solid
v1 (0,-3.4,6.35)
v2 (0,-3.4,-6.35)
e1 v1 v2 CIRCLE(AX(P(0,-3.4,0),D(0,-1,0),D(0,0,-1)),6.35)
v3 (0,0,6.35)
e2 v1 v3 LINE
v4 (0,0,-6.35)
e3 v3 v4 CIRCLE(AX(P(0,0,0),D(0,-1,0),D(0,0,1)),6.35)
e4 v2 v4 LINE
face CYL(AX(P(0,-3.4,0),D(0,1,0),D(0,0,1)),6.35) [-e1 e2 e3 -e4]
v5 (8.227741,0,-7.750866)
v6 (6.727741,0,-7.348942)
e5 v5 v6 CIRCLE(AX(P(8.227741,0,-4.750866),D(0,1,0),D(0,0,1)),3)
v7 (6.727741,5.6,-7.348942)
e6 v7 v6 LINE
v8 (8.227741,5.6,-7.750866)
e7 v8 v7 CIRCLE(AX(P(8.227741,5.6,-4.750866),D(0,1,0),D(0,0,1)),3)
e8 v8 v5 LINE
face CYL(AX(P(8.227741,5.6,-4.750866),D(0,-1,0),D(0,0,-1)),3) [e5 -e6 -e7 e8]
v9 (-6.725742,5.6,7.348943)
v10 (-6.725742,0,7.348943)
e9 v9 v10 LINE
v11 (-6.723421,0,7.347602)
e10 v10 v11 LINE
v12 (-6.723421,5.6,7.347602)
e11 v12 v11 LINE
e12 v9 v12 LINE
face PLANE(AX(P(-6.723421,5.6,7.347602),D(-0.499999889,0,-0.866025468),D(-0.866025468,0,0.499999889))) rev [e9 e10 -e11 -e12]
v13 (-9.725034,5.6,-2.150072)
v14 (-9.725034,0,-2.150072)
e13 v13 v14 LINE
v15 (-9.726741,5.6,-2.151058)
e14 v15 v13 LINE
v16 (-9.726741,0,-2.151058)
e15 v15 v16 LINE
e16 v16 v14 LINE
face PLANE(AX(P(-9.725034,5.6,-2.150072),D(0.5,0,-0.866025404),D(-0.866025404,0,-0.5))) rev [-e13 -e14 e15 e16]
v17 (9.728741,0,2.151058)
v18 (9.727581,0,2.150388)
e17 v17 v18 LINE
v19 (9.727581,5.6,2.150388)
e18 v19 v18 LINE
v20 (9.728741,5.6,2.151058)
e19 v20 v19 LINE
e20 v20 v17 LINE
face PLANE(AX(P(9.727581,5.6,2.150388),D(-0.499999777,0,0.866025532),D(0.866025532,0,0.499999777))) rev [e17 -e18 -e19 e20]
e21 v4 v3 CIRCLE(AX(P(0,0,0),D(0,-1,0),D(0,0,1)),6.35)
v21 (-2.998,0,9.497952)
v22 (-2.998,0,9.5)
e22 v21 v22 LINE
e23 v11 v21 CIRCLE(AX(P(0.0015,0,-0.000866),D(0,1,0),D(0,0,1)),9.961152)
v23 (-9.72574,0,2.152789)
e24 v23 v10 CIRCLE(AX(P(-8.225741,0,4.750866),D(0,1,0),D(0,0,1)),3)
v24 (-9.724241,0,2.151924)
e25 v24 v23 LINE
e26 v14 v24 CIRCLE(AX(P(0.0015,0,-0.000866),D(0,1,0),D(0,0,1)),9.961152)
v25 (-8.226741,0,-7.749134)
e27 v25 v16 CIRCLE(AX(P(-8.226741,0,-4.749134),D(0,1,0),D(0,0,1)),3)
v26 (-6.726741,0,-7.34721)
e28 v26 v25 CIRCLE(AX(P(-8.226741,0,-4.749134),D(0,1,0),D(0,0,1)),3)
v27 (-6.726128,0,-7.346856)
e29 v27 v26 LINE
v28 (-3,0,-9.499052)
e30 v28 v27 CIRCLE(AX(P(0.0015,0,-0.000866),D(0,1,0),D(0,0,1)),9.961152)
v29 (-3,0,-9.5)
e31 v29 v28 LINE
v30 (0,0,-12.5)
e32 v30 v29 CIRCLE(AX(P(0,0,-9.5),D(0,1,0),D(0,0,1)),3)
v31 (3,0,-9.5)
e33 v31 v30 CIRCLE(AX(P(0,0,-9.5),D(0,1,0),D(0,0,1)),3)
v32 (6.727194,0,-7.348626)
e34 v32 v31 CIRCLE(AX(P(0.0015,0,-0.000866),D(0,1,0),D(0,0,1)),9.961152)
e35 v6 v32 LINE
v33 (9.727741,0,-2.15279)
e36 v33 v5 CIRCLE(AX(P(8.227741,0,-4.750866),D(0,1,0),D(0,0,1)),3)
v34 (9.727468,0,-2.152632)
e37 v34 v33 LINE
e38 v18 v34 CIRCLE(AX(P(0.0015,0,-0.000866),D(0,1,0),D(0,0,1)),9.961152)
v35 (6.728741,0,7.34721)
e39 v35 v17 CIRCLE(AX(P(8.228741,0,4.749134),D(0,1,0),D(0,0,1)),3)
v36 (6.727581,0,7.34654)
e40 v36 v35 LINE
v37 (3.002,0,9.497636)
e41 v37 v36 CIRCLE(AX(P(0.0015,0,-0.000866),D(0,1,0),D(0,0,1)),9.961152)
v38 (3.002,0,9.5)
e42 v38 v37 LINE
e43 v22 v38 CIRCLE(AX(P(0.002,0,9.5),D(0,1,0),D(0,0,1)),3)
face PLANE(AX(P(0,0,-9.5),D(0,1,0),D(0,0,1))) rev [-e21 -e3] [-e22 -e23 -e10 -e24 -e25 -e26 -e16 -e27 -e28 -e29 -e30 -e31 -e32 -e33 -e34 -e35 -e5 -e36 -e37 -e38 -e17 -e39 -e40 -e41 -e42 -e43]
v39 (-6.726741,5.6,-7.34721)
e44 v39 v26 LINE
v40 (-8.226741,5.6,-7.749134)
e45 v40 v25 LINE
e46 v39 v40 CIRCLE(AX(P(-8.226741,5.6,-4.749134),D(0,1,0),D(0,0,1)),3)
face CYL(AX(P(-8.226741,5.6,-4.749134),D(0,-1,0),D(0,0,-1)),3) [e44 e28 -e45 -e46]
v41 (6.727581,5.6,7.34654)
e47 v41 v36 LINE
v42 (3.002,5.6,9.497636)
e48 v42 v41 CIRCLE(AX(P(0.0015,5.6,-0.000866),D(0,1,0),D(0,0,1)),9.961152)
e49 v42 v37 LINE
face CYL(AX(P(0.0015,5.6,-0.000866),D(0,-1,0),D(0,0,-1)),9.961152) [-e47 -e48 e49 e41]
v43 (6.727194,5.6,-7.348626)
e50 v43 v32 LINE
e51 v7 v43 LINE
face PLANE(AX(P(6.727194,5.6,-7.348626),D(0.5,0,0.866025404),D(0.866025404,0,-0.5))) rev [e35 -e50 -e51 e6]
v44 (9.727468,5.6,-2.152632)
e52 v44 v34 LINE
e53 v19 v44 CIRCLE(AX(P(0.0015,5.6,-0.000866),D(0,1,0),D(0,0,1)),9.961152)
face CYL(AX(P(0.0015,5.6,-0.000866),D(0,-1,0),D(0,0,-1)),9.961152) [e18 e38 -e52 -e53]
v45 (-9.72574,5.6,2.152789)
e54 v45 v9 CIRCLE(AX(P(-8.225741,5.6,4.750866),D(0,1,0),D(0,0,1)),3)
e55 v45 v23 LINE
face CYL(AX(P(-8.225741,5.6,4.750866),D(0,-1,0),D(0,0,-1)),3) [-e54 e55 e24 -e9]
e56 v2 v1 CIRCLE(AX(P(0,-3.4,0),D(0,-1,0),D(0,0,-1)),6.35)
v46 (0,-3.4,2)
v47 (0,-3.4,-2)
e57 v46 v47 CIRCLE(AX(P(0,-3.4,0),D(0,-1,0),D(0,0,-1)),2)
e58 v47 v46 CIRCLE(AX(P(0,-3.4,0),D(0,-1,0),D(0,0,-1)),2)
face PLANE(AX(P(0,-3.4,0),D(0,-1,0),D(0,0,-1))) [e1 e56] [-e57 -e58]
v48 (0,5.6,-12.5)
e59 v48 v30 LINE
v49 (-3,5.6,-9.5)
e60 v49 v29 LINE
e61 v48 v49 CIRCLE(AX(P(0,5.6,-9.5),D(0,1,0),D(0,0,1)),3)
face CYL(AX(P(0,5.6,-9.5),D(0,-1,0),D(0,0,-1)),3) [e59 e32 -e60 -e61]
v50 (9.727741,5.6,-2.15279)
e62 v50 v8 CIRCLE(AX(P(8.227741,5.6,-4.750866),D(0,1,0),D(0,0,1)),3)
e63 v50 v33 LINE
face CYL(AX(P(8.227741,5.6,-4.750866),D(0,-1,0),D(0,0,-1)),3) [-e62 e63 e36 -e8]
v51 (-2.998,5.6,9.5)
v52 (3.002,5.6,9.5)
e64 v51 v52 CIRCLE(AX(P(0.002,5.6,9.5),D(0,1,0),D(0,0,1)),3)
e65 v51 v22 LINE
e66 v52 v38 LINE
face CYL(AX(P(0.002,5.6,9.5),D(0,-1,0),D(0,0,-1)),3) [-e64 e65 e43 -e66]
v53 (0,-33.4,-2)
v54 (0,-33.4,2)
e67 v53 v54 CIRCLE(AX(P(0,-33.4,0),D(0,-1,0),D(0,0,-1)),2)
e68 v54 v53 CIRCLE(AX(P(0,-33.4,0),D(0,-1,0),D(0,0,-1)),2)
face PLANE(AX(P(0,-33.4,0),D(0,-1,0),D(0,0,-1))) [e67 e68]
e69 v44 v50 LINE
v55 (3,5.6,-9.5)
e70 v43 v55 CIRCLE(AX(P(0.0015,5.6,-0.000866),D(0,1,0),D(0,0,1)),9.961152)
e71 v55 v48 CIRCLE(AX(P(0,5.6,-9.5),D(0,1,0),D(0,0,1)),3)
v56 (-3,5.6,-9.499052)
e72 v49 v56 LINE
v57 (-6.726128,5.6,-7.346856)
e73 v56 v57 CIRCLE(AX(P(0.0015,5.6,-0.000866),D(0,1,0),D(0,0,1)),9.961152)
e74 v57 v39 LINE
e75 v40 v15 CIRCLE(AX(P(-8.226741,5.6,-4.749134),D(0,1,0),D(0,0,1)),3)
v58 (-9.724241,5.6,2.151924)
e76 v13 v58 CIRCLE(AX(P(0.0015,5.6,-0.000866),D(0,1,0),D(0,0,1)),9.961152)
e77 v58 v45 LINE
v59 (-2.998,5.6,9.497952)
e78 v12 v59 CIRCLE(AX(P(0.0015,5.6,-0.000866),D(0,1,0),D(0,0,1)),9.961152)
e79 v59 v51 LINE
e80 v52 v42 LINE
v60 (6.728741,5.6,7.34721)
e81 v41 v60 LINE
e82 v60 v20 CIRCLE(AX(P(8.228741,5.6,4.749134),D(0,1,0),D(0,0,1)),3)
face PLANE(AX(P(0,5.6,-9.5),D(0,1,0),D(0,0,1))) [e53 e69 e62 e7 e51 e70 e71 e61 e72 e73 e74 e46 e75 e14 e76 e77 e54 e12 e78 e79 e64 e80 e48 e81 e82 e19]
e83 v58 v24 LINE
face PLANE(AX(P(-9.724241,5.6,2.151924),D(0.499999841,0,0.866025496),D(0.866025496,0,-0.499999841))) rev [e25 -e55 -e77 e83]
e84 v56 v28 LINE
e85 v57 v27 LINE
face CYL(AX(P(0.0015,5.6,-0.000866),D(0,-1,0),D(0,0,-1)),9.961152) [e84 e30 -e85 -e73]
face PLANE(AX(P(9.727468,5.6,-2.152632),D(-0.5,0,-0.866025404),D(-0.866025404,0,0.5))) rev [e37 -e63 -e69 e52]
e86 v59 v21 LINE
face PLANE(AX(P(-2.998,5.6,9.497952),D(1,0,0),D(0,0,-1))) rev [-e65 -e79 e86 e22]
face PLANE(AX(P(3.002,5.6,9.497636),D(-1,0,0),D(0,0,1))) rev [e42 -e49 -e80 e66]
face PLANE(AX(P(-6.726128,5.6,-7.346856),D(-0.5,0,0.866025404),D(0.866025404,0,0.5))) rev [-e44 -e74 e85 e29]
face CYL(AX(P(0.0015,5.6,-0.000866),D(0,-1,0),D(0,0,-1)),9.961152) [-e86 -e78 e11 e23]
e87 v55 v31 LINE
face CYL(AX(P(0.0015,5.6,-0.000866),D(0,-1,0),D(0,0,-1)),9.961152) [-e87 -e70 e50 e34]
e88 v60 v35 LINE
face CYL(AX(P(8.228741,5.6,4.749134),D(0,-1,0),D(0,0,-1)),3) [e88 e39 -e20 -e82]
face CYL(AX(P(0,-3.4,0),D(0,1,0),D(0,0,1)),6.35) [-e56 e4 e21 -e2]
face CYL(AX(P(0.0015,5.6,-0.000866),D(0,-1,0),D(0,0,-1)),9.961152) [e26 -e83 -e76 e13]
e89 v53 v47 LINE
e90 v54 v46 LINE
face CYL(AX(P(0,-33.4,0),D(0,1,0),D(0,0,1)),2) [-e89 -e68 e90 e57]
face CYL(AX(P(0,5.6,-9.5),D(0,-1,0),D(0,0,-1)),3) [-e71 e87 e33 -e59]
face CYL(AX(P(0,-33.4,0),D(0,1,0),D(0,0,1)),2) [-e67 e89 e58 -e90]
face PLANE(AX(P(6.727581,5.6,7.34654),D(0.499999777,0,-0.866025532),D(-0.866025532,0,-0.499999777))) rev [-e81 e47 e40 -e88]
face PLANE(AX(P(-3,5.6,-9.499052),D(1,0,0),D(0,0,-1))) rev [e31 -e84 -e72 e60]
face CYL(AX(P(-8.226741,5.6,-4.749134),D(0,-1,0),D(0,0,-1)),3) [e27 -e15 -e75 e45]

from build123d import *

# Parameters (mm, degrees)
BOSS_EXTRUDE1_DEPTH = 5.6
SKETCH2_R           = 6.35
BOSS_EXTRUDE2_DEPTH = 3.4
SKETCH3_R           = 2
BOSS_EXTRUDE3_DEPTH = 30


with BuildPart() as part:
    # Sketch1 → Boss-Extrude1 (new body)
    with BuildSketch(Plane(origin=(0, 0, 0), x_dir=(1, 0, 0), z_dir=(0, 1, 0))):
        with BuildLine():
            Line((-9.72424134, -2.15192377), (-9.725740285, -2.152789186))
            ThreePointArc((-9.725740285, -2.152789186), (-10.823817926, -6.250865027), (-6.725742085, -7.348942669))
            Line((-6.725742085, -7.348942669), (-6.723420775, -7.34760246))
            ThreePointArc((-6.723420775, -7.34760246), (-4.978167749, -8.626268935), (-2.998, -9.497952231))
            Line((-2.998, -9.497952231), (-2.998, -9.5))
            ThreePointArc((-2.998, -9.5), (0.002000003, -12.499999996), (3.002, -9.499999993))
            Line((3.002, -9.499999993), (3.002, -9.497636397))
            ThreePointArc((3.002, -9.497636397), (4.982303032, -8.625613539), (6.727581168, -7.346540363))
            Line((6.727581168, -7.346540363), (6.728741336, -7.347210186))
            ThreePointArc((6.728741336, -7.347210186), (10.826817547, -6.249133975), (9.728741336, -2.151057763))
            Line((9.728741336, -2.151057763), (9.727581168, -2.15038794))
            ThreePointArc((9.727581168, -2.15038794), (9.962651964, 0.001128196), (9.727467916, 2.152631955))
            ThreePointArc((9.727467916, 2.152631955), (10.825817547, 6.250866025), (6.727194396, 7.348626461))
            ThreePointArc((6.727194396, 7.348626461), (4.981167779, 8.628000969), (3, 9.5))
            ThreePointArc((3, 9.5), (2e-09, 12.5), (-3, 9.499052498))
            ThreePointArc((-3, 9.499052498), (-4.980665222, 8.626558938), (-6.726128008, 7.346856081))
            ThreePointArc((-6.726128008, 7.346856081), (-10.824817547, 6.249133975), (-9.726741336, 2.151057764))
            Line((-9.726741336, 2.151057764), (-9.725033927, 2.150071991))
            ThreePointArc((-9.725033927, 2.150071991), (-9.959651798, -0.000969188), (-9.72424134, -2.15192377))
        make_face()
    extrude(amount=BOSS_EXTRUDE1_DEPTH)

    # Sketch2 → Boss-Extrude2 (add)
    with BuildSketch(Plane.XZ):
        with Locations(Location((0, 0, 0), (0, 0, 90))):
            Circle(SKETCH2_R)
    extrude(amount=BOSS_EXTRUDE2_DEPTH)

    # Sketch3 → Boss-Extrude3 (add)
    with BuildSketch(Plane.XZ.offset(3.4)):
        with Locations(Location((0, 0, 0), (0, 0, 270))):
            Circle(SKETCH3_R)
    extrude(amount=BOSS_EXTRUDE3_DEPTH)


solid = part.part
